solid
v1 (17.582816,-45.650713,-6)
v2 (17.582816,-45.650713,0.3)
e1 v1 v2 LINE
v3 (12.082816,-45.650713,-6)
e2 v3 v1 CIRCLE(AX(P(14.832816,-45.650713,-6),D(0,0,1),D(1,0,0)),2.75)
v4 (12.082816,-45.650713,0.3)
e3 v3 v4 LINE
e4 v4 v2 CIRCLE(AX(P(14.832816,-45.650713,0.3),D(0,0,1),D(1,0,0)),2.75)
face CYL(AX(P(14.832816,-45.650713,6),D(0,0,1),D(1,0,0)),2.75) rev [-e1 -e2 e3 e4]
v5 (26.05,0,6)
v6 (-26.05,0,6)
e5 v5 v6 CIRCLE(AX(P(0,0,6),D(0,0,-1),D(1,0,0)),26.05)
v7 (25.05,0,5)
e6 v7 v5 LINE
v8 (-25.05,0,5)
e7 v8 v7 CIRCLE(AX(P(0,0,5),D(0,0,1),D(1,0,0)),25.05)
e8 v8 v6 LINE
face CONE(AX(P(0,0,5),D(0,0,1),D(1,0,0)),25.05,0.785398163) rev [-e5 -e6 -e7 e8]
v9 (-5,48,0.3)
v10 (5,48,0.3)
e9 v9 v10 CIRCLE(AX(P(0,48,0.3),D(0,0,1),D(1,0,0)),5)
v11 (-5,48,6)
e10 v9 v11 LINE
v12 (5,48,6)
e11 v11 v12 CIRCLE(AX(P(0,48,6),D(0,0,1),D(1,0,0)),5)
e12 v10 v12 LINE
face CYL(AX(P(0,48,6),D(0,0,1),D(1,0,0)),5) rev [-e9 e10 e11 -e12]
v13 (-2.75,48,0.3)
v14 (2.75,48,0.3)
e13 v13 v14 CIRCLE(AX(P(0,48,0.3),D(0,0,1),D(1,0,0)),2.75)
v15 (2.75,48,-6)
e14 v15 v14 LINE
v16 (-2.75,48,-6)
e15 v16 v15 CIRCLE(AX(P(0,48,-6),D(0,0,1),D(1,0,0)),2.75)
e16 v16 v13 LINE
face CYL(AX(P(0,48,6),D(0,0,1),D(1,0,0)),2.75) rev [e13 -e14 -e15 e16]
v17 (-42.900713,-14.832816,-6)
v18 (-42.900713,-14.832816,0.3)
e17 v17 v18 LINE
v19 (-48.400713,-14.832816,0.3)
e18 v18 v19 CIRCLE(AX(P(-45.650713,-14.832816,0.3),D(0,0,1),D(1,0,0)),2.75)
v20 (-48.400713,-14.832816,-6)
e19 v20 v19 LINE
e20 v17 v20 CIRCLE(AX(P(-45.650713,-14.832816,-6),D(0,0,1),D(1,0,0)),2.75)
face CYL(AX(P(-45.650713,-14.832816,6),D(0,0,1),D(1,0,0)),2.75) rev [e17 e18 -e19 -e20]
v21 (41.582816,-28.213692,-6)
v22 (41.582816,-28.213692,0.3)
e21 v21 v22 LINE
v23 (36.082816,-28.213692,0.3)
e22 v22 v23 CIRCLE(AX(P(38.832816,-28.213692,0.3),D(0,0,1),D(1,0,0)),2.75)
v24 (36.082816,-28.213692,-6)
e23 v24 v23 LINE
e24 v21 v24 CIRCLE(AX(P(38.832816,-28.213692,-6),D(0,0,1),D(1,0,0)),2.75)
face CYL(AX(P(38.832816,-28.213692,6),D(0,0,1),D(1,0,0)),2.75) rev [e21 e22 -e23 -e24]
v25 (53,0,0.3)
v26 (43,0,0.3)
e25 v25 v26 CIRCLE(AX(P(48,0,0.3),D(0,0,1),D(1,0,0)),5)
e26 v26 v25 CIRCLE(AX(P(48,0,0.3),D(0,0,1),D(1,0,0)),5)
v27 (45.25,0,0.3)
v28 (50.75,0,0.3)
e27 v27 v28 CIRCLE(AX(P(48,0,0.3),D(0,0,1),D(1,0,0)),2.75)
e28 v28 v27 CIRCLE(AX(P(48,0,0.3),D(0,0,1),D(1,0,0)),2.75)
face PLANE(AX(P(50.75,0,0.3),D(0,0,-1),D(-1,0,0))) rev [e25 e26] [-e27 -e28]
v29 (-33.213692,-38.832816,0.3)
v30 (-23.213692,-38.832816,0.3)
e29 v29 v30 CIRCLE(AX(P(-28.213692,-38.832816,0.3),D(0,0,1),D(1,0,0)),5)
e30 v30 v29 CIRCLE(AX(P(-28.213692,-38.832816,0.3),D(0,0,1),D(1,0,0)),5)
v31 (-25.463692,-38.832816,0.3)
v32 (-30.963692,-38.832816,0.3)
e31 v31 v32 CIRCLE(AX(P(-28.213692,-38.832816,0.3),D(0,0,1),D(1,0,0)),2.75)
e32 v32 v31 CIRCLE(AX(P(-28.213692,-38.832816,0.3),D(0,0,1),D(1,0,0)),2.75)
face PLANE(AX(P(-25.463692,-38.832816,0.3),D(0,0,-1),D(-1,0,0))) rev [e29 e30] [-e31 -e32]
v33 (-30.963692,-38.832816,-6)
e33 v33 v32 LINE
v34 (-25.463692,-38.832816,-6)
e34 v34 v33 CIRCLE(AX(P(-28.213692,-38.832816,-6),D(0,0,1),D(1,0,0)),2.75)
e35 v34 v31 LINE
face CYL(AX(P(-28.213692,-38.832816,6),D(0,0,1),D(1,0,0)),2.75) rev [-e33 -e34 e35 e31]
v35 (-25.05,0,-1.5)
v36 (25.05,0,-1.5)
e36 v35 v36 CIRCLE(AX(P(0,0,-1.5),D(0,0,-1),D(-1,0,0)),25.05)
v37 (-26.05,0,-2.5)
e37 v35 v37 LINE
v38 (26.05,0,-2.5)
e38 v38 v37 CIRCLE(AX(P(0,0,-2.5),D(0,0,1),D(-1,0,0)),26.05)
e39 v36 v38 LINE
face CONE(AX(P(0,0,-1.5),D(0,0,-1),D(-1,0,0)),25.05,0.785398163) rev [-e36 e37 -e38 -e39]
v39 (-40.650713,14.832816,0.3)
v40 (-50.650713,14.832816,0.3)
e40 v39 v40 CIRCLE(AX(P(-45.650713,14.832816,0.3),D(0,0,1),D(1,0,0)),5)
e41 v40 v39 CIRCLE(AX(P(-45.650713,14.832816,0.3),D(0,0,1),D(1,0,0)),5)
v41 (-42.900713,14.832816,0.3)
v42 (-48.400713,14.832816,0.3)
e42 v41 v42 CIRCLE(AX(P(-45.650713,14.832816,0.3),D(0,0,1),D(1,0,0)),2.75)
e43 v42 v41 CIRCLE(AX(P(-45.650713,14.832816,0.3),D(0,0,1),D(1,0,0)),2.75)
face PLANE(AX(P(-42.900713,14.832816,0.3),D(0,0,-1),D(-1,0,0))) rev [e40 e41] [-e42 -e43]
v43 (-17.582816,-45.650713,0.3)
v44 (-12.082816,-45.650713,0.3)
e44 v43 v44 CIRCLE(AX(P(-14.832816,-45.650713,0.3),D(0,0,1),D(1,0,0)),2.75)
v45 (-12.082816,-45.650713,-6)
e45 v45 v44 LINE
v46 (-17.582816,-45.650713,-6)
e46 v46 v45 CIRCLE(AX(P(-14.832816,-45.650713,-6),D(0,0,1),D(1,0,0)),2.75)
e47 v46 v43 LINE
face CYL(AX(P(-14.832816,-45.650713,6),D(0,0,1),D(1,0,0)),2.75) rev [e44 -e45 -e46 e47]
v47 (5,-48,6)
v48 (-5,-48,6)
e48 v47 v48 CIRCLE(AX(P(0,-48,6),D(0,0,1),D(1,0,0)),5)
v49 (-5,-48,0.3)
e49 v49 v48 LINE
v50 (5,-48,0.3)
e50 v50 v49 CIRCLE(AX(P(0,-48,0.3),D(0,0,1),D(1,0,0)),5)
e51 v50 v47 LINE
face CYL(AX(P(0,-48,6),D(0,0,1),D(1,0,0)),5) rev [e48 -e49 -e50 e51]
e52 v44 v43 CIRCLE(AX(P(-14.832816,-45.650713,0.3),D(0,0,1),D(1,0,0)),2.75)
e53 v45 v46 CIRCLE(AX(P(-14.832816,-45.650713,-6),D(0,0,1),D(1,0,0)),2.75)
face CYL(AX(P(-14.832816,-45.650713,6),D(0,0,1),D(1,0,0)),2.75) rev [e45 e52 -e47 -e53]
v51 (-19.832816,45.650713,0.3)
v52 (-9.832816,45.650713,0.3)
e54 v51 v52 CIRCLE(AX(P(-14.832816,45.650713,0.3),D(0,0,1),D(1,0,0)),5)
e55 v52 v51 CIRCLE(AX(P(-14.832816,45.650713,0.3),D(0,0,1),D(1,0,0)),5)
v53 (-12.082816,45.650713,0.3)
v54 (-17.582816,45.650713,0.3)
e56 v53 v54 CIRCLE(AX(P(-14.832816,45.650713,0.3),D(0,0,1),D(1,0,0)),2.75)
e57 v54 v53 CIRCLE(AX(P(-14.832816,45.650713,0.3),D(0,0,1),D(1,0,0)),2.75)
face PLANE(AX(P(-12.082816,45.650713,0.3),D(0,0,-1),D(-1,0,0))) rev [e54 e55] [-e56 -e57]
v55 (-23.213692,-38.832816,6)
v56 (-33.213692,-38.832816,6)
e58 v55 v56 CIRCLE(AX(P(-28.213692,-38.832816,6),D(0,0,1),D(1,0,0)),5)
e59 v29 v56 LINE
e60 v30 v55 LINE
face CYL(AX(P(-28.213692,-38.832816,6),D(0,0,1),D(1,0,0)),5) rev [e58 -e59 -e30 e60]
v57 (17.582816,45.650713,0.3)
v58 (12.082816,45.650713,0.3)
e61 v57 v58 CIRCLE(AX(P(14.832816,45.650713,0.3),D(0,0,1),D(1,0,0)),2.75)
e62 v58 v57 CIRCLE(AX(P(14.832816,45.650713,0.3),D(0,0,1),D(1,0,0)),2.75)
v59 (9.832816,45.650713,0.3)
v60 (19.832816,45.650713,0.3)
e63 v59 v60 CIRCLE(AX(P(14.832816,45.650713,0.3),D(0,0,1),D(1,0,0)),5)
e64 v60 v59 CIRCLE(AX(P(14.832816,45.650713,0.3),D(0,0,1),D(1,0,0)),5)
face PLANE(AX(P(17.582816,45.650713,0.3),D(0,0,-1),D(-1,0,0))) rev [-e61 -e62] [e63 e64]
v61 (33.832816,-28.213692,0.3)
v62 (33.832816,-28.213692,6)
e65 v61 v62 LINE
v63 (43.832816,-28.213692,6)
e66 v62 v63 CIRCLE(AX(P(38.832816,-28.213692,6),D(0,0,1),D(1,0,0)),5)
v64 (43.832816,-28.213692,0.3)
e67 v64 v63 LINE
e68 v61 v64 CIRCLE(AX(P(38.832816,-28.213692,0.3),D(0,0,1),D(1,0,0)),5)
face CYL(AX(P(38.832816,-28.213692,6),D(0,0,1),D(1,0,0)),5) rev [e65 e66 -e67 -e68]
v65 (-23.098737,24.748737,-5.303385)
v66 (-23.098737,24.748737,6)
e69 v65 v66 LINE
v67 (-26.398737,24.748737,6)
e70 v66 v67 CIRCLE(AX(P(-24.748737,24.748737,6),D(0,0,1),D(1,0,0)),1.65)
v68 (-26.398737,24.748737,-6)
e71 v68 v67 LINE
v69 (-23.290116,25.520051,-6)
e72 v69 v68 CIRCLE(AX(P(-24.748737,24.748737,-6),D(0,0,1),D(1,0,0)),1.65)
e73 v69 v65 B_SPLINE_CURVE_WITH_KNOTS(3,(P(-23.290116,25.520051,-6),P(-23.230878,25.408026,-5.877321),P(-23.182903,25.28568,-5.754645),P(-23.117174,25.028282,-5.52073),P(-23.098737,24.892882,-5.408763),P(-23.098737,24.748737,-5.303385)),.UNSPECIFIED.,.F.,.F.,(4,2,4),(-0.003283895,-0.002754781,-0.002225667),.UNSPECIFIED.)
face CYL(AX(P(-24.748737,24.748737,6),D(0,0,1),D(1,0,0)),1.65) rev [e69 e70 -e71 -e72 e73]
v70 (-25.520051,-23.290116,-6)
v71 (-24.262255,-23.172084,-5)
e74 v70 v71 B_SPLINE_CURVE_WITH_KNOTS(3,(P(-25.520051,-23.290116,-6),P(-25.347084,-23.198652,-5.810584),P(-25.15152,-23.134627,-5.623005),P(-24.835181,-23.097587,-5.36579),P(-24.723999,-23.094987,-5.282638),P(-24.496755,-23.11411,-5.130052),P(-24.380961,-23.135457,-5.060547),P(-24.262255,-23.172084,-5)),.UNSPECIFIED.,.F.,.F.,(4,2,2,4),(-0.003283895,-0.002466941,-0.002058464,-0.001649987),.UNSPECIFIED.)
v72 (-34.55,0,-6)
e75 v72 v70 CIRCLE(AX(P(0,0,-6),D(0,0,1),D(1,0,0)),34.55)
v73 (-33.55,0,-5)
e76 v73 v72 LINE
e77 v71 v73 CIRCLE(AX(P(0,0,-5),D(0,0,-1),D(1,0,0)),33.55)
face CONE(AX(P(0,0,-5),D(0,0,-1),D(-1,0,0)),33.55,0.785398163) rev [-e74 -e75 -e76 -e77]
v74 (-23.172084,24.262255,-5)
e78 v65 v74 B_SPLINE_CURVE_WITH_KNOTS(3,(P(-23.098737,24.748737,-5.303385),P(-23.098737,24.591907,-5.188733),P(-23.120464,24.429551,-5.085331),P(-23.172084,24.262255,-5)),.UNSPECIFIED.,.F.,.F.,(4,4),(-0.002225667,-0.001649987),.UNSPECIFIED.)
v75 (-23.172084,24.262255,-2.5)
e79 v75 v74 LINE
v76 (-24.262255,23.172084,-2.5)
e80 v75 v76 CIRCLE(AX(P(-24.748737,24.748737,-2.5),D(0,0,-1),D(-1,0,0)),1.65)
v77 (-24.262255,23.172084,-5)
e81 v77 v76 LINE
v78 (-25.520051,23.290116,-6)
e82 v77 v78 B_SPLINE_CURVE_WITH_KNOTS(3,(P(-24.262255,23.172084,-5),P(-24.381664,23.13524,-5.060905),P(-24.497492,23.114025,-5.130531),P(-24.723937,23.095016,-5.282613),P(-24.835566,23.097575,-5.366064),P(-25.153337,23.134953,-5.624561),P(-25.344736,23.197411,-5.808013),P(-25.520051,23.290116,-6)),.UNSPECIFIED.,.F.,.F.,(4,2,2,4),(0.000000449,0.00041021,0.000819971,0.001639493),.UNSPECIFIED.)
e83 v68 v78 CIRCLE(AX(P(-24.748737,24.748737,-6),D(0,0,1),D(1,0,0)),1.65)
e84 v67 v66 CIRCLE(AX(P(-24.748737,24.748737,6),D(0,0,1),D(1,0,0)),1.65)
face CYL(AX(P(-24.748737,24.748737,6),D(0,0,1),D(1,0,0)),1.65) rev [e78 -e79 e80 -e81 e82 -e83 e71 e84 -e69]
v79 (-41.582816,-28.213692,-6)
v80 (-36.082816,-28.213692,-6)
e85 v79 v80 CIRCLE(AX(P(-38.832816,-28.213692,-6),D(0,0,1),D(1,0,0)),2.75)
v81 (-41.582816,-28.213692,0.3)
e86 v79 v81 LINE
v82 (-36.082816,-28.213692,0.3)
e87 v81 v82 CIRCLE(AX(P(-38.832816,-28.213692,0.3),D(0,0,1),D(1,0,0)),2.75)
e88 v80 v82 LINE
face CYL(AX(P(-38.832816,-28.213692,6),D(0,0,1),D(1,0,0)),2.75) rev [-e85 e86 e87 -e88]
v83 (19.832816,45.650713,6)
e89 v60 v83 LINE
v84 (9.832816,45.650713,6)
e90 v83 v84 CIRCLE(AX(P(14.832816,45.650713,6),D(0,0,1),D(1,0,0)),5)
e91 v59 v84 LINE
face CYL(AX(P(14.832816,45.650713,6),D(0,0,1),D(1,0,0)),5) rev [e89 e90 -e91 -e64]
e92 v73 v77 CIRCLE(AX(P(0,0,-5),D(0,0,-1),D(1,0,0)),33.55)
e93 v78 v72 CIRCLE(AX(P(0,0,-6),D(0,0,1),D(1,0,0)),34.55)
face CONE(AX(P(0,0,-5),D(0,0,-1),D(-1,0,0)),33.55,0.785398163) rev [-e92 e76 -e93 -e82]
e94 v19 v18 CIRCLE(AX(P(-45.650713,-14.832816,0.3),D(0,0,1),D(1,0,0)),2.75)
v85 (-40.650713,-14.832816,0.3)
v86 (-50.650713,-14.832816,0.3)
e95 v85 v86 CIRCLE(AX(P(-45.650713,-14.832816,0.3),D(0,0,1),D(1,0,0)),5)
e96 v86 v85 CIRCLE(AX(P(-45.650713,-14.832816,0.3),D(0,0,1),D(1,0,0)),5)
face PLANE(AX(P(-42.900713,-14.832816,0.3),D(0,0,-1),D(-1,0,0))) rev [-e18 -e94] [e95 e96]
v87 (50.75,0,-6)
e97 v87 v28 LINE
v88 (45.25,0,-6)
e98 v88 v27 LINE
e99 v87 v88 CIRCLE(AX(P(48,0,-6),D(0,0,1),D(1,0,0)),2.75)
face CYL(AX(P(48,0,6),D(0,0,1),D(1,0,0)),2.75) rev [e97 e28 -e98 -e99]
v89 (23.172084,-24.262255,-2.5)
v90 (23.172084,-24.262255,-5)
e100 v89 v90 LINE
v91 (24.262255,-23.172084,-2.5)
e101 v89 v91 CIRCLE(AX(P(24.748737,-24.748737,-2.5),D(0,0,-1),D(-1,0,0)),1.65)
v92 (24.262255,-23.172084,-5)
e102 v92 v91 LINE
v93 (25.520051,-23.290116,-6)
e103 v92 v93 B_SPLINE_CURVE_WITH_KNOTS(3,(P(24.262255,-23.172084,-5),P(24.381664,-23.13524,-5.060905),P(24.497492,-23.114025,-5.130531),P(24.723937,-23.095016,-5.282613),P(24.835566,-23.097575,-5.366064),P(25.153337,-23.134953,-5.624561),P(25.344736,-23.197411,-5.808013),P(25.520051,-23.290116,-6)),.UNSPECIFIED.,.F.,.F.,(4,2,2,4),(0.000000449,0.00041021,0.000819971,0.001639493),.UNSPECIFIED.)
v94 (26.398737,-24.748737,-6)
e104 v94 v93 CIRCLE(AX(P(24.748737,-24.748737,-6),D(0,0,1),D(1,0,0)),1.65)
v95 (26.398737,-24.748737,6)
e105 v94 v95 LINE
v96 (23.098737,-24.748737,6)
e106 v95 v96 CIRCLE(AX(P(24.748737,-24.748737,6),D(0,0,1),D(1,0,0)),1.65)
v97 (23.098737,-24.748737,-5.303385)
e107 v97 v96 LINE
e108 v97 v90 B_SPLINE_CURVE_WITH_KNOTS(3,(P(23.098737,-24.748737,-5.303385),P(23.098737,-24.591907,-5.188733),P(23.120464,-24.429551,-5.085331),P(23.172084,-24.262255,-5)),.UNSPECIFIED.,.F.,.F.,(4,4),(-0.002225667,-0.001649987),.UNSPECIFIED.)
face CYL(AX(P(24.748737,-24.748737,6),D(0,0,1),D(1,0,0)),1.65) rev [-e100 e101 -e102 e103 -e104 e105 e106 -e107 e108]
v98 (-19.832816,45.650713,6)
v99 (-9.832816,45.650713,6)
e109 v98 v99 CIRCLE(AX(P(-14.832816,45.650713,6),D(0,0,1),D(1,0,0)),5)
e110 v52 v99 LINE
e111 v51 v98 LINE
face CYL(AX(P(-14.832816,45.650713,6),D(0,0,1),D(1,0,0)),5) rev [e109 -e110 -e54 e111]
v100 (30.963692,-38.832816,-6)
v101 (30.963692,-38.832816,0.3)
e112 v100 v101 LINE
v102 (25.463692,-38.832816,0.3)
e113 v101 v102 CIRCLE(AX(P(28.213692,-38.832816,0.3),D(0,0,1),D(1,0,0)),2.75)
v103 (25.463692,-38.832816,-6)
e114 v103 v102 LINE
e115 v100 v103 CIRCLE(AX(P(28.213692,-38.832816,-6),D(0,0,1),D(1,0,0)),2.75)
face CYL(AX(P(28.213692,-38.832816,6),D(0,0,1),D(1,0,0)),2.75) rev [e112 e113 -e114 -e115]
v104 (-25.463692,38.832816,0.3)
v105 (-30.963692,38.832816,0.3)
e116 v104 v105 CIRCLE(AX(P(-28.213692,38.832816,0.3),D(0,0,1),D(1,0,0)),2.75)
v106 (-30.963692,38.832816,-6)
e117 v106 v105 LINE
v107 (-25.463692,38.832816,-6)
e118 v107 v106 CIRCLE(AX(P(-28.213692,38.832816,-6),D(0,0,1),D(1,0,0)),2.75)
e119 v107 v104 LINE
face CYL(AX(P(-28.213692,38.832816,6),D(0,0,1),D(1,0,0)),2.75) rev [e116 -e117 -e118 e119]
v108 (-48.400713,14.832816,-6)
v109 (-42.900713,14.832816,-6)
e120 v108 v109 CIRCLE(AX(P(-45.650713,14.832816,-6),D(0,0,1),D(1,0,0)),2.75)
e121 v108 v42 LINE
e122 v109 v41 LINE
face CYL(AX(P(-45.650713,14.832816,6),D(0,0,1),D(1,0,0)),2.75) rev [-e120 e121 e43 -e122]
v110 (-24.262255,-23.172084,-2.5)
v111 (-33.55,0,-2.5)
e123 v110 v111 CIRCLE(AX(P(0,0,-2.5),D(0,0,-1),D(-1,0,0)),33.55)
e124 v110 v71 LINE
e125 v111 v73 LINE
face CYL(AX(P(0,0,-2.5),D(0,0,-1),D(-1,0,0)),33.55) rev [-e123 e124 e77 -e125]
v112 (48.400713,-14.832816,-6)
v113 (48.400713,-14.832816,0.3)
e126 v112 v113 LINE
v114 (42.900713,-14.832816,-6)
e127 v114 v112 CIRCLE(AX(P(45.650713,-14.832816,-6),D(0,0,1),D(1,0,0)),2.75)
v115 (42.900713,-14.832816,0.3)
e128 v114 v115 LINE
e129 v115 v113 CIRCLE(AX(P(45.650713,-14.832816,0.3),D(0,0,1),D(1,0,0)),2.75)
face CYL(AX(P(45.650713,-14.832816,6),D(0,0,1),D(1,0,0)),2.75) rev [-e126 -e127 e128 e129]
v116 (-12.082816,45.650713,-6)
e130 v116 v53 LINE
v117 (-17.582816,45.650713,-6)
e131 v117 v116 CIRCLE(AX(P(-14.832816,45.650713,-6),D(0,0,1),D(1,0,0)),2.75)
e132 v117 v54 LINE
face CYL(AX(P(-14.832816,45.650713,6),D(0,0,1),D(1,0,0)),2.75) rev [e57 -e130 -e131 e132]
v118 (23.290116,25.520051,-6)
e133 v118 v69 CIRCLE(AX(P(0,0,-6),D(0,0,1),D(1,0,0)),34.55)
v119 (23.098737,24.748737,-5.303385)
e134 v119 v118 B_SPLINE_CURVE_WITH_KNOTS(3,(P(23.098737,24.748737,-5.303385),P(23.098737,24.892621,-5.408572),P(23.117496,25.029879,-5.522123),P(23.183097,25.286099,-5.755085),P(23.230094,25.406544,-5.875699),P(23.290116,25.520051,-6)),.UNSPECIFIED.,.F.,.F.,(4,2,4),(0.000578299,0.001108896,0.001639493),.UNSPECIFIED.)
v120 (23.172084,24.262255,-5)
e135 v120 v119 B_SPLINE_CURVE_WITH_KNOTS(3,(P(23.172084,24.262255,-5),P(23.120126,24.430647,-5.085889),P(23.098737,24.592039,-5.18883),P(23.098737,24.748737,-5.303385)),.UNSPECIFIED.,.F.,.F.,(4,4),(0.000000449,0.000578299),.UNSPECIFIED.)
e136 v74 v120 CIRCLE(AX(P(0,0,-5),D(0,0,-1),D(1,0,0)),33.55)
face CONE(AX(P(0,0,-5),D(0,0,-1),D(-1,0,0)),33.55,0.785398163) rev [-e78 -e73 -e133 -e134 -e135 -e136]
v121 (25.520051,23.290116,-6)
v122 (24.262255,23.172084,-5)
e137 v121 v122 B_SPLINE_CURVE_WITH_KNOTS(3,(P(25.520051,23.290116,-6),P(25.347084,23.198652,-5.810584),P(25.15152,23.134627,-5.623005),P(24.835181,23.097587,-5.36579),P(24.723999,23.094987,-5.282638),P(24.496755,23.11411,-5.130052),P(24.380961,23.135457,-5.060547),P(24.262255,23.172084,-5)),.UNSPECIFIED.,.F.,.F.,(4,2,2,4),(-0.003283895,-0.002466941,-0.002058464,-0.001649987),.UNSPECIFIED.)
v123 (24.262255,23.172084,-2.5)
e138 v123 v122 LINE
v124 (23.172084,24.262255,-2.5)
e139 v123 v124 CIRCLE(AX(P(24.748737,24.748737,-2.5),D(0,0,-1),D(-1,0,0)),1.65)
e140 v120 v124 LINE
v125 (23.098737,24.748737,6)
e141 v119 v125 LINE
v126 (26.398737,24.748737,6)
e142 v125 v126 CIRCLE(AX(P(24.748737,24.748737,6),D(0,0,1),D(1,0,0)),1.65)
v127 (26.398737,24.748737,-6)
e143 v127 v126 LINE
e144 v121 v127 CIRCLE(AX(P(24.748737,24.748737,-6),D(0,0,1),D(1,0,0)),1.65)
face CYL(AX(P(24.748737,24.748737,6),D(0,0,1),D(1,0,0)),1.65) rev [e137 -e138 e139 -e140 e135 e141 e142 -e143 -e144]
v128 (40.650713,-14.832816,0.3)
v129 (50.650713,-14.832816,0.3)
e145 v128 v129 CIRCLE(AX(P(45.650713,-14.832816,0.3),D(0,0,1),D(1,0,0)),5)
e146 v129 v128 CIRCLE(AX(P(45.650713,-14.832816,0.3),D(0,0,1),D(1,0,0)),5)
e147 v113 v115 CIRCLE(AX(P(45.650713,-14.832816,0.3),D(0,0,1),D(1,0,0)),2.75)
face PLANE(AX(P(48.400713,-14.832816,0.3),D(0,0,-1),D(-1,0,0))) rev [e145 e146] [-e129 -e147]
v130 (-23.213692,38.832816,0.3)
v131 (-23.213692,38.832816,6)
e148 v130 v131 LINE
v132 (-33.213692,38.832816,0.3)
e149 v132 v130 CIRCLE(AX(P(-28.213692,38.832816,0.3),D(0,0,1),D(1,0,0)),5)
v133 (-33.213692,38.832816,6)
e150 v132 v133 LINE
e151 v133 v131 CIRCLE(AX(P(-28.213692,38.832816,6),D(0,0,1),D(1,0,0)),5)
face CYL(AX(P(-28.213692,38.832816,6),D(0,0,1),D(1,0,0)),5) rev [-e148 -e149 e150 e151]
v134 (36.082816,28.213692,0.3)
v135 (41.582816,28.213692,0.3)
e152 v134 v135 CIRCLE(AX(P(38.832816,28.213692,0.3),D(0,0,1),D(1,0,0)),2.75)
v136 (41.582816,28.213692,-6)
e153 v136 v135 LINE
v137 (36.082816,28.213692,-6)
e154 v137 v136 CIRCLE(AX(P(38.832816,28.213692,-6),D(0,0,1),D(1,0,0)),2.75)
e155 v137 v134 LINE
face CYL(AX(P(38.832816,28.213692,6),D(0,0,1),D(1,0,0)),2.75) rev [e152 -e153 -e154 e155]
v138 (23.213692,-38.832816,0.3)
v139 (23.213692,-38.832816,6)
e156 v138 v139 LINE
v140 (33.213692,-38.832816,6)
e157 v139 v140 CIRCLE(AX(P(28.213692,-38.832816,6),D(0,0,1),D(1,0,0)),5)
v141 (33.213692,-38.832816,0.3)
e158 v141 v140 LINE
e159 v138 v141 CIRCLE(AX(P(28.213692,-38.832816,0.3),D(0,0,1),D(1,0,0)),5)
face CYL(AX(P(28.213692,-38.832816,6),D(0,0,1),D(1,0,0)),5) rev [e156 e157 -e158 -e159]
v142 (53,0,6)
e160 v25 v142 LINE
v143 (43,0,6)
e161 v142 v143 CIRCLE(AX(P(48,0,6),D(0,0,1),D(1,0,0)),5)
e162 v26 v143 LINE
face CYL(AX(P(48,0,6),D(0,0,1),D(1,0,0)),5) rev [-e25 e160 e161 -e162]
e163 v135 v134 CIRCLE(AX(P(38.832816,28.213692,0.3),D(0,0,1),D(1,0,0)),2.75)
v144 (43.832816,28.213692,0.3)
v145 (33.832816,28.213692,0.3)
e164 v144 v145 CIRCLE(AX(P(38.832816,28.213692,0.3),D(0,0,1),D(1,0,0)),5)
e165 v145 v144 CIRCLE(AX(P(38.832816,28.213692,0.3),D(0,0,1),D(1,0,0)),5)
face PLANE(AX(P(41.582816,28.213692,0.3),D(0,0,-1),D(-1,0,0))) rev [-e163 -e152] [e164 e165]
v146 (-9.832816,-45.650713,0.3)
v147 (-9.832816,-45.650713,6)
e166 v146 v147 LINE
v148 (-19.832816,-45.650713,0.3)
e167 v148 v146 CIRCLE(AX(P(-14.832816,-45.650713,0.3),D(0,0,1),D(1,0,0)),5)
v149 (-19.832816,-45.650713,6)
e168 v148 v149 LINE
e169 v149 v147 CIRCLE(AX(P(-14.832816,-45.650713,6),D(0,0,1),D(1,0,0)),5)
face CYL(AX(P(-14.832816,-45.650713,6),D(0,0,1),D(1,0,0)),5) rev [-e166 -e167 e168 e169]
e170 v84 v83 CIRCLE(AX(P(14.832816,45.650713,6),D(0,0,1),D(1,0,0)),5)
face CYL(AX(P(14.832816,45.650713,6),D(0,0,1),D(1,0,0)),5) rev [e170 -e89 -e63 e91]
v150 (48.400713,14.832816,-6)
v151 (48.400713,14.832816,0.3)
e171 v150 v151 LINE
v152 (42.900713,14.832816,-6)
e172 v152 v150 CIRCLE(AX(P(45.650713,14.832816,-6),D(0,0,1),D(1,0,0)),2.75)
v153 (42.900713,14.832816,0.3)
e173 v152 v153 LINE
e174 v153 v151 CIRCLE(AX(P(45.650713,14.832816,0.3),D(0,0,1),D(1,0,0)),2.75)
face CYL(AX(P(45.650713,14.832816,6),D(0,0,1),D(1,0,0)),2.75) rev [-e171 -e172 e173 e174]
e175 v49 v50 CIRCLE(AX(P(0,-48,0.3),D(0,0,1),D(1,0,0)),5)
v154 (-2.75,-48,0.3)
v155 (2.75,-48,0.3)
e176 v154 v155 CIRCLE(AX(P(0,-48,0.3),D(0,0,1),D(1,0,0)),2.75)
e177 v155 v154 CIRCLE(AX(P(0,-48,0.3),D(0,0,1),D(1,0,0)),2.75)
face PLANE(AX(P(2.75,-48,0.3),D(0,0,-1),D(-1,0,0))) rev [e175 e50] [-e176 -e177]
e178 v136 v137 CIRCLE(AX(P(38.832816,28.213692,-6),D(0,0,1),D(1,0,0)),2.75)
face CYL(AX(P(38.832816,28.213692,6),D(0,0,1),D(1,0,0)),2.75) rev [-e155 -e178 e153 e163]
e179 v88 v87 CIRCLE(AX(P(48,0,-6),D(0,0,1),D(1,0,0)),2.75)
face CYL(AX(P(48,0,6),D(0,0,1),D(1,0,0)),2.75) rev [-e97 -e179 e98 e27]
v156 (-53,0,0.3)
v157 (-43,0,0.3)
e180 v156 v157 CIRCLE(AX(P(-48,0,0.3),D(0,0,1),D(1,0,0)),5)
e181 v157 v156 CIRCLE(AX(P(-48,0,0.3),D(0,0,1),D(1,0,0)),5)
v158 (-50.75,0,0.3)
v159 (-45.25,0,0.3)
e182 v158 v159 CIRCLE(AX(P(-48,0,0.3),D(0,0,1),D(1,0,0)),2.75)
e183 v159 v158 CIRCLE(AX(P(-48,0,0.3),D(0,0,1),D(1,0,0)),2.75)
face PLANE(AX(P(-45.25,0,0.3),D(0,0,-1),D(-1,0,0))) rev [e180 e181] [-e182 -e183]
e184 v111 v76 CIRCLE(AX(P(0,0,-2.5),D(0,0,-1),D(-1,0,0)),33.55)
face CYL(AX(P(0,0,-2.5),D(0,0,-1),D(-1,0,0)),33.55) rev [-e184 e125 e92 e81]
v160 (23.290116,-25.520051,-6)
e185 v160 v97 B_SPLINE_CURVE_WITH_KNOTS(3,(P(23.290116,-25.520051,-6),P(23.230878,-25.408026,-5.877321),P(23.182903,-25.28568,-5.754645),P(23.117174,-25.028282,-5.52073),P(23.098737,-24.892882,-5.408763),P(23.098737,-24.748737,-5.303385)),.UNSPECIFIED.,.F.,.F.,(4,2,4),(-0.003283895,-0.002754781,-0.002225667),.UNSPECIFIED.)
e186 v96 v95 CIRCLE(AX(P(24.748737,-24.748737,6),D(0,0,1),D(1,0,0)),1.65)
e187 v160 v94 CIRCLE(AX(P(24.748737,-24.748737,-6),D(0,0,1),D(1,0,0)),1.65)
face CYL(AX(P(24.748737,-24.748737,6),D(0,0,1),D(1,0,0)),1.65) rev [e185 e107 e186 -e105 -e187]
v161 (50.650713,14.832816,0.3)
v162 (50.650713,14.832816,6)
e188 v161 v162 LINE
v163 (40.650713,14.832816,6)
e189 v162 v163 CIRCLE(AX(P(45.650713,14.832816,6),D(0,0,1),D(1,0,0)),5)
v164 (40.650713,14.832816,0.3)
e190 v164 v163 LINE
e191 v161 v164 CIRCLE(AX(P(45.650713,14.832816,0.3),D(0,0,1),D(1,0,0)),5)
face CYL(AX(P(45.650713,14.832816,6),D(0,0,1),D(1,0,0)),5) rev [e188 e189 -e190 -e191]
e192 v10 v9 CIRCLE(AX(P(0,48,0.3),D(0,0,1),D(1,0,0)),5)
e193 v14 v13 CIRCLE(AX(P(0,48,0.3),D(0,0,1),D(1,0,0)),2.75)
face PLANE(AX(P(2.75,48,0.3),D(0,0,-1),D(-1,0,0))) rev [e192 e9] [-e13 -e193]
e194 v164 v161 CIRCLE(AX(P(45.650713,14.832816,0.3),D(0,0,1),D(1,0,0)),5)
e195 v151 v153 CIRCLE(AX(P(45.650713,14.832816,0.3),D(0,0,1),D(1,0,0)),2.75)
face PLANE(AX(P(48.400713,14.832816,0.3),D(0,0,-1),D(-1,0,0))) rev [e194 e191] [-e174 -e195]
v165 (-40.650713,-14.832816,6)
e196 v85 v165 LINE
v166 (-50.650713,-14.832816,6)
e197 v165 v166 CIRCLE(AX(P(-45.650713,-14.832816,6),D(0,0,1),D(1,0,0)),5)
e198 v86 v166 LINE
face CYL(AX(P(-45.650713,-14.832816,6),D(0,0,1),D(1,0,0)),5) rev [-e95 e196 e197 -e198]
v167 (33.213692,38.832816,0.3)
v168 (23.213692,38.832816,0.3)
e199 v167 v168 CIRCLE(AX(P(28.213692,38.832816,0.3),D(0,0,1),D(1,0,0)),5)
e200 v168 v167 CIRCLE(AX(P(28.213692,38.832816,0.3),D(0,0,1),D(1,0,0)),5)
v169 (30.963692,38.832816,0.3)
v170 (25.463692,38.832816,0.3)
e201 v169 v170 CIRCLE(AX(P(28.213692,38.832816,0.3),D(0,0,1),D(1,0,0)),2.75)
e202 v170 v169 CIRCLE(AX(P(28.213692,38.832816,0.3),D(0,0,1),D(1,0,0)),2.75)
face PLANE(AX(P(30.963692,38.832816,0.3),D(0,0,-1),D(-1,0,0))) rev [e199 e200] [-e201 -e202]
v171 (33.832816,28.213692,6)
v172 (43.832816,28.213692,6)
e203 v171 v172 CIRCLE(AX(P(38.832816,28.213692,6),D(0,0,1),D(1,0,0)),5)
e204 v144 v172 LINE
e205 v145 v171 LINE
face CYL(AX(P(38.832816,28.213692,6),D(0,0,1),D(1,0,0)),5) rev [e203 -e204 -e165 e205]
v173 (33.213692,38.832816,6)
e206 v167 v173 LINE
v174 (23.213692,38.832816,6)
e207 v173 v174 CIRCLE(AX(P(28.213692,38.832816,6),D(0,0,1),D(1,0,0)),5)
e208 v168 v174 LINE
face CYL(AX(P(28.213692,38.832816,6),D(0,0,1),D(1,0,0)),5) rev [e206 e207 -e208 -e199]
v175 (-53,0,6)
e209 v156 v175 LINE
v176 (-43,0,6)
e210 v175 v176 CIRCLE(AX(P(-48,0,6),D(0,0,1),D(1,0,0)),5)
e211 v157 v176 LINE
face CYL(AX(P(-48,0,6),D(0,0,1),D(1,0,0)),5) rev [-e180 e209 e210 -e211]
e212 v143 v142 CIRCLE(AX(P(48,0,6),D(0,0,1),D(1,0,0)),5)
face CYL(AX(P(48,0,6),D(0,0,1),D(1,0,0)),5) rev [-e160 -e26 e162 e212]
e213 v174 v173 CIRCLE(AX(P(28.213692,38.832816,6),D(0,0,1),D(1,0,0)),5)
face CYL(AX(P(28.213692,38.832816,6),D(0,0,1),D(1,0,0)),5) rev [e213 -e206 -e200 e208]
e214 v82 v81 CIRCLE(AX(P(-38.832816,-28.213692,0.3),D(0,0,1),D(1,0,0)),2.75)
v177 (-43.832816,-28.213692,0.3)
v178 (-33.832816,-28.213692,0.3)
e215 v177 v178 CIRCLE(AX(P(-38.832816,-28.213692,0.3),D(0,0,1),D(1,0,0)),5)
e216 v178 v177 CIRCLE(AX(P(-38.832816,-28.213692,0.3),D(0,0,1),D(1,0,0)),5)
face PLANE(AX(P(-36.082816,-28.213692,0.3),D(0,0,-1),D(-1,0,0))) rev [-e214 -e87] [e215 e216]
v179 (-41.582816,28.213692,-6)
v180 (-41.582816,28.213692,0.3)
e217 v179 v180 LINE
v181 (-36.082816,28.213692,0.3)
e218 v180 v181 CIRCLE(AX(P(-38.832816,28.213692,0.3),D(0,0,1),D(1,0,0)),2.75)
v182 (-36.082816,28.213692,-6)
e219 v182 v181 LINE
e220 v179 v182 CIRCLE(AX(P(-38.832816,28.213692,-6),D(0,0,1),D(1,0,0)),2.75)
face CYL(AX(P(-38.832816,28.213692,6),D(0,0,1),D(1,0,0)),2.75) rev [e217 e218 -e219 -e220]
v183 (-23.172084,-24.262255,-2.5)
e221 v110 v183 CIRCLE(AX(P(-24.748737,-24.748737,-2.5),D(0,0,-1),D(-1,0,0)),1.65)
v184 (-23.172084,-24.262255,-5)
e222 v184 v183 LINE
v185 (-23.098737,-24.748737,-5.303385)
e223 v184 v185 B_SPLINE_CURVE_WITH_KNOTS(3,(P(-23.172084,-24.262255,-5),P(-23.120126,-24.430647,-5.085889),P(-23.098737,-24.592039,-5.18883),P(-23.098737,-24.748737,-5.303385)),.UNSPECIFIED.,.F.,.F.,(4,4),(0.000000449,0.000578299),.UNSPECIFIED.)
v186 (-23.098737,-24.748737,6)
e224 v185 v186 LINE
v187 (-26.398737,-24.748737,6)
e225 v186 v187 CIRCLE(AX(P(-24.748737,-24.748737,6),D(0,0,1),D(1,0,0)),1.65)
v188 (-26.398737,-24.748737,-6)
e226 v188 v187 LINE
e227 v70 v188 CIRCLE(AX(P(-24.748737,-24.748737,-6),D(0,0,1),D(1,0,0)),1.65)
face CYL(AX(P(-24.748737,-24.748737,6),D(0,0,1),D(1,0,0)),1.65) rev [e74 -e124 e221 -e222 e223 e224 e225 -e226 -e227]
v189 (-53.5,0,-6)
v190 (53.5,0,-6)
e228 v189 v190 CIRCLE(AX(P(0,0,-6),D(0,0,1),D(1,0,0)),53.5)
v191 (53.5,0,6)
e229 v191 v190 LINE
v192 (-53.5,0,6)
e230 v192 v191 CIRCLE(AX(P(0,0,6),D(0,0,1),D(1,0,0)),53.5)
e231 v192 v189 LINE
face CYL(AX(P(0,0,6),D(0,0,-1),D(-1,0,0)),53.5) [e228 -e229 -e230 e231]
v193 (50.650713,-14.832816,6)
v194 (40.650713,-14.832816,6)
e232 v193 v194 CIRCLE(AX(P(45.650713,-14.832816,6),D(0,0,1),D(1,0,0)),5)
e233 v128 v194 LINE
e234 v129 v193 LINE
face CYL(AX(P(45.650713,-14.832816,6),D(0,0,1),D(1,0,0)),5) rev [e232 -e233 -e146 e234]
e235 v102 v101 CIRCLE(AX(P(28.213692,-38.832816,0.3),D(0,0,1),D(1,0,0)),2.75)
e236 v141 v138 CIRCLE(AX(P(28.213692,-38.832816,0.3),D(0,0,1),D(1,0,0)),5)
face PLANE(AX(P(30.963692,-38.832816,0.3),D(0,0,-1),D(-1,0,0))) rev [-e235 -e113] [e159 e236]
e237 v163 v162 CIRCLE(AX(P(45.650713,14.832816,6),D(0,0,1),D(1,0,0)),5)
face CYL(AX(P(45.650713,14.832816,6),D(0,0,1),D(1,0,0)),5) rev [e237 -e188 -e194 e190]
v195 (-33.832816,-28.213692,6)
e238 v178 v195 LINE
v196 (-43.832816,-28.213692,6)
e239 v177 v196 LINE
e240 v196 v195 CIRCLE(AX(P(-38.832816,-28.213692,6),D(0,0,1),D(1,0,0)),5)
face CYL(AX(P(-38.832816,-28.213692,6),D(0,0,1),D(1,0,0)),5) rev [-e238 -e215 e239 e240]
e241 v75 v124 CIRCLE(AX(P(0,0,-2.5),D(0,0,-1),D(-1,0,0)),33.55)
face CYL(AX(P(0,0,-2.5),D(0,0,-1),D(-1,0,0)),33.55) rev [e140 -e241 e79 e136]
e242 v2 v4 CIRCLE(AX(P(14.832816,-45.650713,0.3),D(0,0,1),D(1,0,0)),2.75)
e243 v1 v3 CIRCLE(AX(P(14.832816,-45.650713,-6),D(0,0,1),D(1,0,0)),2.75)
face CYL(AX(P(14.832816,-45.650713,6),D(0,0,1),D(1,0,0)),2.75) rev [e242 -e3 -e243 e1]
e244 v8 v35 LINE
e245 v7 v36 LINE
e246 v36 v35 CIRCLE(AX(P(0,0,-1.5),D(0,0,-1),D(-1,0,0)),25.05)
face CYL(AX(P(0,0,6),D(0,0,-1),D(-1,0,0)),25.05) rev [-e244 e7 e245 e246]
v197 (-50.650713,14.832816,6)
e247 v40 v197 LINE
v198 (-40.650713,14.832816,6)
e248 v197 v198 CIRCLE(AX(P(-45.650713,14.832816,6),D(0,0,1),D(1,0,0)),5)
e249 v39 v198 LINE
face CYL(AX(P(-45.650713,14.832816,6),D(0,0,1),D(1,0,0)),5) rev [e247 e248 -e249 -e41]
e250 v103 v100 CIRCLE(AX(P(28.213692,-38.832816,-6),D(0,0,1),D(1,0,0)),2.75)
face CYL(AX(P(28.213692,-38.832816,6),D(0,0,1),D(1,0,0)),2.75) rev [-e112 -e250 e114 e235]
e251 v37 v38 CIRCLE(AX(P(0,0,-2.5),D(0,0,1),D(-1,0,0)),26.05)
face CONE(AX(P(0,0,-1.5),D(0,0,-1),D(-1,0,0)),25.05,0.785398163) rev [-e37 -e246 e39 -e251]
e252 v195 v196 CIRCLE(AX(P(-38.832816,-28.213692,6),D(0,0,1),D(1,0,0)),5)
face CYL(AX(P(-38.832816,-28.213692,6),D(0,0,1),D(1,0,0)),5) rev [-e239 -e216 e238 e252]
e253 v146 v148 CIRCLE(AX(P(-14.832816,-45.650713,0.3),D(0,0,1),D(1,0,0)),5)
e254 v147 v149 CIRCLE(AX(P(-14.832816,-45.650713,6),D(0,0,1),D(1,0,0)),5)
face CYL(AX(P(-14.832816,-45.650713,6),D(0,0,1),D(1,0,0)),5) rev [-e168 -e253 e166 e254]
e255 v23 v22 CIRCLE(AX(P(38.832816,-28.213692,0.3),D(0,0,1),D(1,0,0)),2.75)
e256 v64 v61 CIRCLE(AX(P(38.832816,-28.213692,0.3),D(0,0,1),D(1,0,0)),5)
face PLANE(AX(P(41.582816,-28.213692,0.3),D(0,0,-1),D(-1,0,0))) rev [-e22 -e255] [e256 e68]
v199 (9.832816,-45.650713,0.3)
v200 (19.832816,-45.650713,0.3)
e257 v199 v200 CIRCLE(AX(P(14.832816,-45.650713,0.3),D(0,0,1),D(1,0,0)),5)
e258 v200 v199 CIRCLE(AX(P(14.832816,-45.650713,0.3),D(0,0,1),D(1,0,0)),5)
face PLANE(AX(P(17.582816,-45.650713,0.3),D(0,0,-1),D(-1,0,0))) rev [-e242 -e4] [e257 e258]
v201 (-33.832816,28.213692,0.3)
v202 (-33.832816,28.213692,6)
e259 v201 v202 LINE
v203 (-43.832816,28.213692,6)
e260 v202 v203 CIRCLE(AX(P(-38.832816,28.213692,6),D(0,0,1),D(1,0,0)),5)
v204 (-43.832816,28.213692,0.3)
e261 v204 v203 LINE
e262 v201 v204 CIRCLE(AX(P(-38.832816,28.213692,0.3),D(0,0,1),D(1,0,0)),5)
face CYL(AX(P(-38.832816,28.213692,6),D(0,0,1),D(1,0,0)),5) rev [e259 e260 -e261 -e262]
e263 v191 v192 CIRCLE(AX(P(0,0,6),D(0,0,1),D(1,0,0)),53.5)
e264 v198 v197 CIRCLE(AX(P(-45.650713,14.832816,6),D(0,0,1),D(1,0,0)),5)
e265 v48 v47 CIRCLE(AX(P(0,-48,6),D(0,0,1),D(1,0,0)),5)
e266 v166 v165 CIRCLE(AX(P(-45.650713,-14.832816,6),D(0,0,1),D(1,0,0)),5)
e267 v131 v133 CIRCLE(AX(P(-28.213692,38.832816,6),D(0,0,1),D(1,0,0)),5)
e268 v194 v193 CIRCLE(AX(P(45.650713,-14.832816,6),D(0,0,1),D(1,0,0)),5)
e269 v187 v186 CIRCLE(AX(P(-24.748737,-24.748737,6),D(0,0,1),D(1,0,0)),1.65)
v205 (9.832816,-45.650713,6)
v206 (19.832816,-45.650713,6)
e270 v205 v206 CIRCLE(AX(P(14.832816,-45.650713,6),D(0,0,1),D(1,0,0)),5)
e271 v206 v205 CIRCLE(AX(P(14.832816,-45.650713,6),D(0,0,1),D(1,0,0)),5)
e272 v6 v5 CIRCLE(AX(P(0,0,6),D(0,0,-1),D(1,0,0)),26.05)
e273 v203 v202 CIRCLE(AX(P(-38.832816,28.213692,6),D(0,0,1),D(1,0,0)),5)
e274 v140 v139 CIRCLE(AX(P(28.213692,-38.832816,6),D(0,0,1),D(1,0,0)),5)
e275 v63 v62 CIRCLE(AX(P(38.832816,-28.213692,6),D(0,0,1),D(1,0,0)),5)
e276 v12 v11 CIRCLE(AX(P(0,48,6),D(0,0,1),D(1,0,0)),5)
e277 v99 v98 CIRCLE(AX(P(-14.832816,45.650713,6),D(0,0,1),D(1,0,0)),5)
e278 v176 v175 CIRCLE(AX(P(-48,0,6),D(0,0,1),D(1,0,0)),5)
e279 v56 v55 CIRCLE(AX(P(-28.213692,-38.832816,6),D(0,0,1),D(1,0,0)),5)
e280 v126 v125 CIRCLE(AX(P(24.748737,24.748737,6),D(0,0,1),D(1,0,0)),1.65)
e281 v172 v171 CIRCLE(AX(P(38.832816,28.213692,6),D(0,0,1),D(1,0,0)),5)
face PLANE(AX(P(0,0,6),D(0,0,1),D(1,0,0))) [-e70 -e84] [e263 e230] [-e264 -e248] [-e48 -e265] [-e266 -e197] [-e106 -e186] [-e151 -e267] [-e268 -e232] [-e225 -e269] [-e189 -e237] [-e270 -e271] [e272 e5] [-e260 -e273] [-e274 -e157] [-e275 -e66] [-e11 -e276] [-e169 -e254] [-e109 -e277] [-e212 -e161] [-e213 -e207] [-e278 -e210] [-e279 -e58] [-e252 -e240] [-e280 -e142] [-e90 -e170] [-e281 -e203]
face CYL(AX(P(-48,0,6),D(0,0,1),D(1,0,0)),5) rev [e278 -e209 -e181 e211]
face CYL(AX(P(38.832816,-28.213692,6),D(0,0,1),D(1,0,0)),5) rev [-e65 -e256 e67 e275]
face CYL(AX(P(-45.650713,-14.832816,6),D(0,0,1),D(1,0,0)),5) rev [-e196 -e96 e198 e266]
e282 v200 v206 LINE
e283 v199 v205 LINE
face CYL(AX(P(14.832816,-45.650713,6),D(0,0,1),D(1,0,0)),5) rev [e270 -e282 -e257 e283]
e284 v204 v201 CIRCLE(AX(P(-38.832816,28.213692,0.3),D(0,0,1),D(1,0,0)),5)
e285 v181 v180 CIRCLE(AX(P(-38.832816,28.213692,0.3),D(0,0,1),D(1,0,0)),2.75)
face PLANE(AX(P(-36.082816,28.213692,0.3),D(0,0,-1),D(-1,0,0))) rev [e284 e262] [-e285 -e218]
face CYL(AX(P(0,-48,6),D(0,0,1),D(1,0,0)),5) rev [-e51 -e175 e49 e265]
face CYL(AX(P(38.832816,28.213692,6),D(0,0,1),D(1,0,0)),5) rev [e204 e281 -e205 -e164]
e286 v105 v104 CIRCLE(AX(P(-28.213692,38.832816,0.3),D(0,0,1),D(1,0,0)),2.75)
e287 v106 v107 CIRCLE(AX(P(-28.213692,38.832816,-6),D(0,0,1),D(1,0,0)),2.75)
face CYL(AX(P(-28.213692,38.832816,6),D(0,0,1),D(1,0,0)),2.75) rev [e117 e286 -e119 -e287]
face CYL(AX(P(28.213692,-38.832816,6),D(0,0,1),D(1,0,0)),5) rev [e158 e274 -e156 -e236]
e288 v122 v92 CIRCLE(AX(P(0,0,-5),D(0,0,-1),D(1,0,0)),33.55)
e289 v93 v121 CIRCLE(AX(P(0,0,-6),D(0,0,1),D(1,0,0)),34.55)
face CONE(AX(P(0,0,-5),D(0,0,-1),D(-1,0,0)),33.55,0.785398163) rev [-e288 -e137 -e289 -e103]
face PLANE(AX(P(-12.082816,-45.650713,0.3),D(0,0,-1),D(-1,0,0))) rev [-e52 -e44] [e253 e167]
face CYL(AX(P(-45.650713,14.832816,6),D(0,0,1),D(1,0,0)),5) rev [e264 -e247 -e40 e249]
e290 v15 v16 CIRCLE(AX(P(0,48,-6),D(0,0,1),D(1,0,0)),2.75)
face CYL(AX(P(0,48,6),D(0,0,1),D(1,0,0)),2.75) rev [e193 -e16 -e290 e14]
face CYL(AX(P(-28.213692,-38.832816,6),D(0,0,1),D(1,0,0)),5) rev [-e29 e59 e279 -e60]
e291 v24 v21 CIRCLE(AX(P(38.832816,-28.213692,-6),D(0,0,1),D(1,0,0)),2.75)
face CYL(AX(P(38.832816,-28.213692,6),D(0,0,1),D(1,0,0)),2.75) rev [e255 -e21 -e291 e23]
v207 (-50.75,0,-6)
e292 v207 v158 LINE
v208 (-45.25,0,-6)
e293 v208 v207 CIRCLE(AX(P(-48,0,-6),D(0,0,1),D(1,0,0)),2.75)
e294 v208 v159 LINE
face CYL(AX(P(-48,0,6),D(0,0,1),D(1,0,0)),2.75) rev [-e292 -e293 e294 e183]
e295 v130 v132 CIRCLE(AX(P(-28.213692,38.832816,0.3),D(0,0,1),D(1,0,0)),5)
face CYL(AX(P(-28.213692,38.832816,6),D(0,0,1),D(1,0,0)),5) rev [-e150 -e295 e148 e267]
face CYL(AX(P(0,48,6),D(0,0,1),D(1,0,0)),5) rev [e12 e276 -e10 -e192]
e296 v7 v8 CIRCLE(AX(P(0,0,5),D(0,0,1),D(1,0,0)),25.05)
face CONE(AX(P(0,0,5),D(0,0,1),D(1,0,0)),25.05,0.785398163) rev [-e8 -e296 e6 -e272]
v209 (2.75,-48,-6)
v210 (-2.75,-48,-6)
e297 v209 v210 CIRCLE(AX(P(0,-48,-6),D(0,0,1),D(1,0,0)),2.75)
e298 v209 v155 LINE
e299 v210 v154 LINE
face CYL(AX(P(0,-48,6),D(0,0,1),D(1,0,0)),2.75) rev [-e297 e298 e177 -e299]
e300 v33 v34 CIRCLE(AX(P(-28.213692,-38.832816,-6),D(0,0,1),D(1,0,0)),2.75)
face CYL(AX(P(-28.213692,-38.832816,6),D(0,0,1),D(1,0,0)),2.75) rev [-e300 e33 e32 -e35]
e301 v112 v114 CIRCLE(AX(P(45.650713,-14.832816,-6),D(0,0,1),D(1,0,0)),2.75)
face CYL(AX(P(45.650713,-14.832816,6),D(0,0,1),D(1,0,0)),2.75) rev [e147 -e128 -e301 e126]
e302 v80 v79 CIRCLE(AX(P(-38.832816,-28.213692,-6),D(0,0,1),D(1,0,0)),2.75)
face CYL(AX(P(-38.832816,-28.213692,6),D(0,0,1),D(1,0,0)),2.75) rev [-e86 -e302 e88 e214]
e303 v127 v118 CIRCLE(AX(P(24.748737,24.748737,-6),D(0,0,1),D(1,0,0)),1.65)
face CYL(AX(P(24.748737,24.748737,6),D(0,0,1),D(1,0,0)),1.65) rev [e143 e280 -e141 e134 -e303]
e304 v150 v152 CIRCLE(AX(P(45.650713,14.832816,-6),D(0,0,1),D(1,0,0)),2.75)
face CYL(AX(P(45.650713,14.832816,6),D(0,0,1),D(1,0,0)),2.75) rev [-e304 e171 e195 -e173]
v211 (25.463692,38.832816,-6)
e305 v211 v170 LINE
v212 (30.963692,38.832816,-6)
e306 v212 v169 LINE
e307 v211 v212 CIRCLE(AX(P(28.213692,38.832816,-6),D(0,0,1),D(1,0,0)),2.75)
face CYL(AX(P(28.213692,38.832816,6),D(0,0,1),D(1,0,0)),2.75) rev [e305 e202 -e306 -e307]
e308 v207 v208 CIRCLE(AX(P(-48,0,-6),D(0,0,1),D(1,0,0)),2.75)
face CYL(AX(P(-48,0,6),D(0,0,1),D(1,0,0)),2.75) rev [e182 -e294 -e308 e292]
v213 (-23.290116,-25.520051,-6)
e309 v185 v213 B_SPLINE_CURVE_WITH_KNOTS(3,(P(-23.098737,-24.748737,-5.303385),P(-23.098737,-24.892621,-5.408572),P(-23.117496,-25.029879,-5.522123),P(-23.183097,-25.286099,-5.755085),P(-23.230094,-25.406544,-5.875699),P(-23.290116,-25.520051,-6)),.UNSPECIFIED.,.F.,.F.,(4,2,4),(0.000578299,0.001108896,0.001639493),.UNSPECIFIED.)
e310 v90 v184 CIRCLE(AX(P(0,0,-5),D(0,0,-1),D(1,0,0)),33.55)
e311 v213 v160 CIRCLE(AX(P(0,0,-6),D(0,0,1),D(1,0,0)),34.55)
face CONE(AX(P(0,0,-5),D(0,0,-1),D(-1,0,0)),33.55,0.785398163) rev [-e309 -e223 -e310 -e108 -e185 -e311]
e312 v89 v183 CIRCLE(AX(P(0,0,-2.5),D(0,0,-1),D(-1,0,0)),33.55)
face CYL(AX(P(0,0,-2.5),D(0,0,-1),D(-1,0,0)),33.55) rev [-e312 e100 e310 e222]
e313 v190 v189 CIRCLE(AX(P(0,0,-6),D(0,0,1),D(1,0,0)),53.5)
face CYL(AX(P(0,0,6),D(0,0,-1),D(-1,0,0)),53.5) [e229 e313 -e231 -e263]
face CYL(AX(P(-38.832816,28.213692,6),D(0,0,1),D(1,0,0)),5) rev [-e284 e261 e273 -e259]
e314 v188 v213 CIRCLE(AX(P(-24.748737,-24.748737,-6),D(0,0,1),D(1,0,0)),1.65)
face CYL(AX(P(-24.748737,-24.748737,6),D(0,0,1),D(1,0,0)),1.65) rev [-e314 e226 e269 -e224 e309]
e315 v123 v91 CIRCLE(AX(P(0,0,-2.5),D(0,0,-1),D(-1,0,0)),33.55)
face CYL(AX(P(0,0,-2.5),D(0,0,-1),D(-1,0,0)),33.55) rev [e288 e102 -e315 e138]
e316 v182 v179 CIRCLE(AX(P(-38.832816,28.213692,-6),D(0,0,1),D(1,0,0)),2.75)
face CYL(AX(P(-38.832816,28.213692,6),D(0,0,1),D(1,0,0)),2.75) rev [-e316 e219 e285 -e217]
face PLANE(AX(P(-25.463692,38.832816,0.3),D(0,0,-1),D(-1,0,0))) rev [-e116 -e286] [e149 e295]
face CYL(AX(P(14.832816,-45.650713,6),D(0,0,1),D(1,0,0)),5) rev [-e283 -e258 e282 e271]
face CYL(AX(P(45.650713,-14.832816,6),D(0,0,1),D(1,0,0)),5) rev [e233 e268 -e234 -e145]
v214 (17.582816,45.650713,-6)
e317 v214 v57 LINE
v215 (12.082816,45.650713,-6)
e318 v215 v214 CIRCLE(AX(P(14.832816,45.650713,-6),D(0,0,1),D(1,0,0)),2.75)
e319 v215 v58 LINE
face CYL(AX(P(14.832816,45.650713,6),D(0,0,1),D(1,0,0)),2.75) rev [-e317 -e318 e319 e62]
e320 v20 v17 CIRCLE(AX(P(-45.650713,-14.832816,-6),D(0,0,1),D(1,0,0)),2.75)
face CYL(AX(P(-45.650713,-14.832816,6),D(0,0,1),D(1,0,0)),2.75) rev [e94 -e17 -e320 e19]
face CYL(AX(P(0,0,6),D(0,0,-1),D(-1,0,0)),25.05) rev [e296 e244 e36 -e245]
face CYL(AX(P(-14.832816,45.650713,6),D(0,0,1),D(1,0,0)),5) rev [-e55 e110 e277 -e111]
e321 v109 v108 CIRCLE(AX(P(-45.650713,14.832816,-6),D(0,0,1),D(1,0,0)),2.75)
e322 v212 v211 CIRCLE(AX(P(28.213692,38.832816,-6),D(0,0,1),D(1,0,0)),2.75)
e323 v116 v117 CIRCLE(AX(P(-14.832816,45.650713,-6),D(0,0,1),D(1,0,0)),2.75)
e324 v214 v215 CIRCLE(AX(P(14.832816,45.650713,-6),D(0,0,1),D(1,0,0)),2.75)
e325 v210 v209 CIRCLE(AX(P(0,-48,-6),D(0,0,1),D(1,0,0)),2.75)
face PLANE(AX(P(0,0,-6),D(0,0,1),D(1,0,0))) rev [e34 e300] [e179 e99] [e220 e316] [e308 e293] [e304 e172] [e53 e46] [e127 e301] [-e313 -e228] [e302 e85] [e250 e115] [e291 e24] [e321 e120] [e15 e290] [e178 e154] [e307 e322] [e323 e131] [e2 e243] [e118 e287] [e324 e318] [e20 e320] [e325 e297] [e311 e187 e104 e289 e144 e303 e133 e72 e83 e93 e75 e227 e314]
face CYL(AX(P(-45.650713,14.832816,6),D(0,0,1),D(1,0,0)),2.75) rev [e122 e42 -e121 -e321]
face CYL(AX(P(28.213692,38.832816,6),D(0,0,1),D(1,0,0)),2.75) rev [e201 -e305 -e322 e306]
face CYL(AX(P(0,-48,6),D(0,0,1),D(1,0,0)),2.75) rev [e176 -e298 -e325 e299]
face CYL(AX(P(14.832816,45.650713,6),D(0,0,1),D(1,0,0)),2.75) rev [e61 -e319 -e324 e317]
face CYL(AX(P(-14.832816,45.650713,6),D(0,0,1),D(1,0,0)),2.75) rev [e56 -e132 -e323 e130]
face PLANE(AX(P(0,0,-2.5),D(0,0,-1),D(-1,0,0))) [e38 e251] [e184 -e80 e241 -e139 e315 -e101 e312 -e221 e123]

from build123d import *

# Parameters (mm, degrees)
SKETCH_1_R                = 53.5
SKETCH_1_R_2              = 25.05
EXTRUDE_1_DEPTH           = 6
HOLE_WIZARD_1_D           = 5.5
HOLE_WIZARD_1_CBORE_D     = 10
HOLE_WIZARD_1_CBORE_DEPTH = 5.7
SKETCH_6_R                = 33.55
CUT_EXTRUDE_1_DEPTH       = 3.5
CHAMFER_1_SIZE            = 1
HOLE_WIZARD_M4_1_D        = 3.3
PATTERN_CIRCULAR_1_COUNT  = 20
PATTERN_CIRCULAR_2_COUNT  = 4


with BuildPart() as part:
    # 草图1 → 凸台-拉伸1 (new, symmetric)
    with BuildSketch(Plane.XY):
        Circle(SKETCH_1_R)
        Circle(SKETCH_1_R_2, mode=Mode.SUBTRACT)
    extrude(amount=EXTRUDE_1_DEPTH, both=True)

    # 打孔尺寸(%根据)内六角圆柱头螺钉的类型1 (through all)
    with Locations(Plane.XY.offset(6)):
        with Locations((0, 48)):
            hole_wizard_1 = CounterBoreHole(HOLE_WIZARD_1_D / 2, HOLE_WIZARD_1_CBORE_D / 2, HOLE_WIZARD_1_CBORE_DEPTH)

    # 草图6 → 切除-拉伸1 (cut)
    with BuildSketch(Plane(origin=(0, 0, -6), x_dir=(-1, 0, 0), z_dir=(0, 0, -1))):
        Circle(SKETCH_6_R)
    extrude(amount=-CUT_EXTRUDE_1_DEPTH, mode=Mode.SUBTRACT)

    # 倒角1
    chamfer_1_edges = [part.edges().sort_by_distance(p)[0] for p in [
        (-25.05, 0, -2.5),
        (33.55, 0, -6),
        (-25.05, 0, 6),
    ]]
    chamfer(chamfer_1_edges, length=CHAMFER_1_SIZE)

    # M4 螺纹孔1 (through all)
    with Locations(Plane.XY.offset(6)):
        with Locations((24.748737342, 24.748737342)):
            hole_wizard_m4_1 = Hole(HOLE_WIZARD_M4_1_D / 2)

    # 阵列(圆周)1: 打孔尺寸(%根据)内六角圆柱头螺钉的类型1 ×20 about axis
    pattern_circular_1_axis = Axis((0, 0, 0), (0, 0, 1))
    for i in range(1, PATTERN_CIRCULAR_1_COUNT):
        add(hole_wizard_1.rotate(pattern_circular_1_axis, i * 360 / PATTERN_CIRCULAR_1_COUNT), mode=Mode.SUBTRACT)

    # 阵列(圆周)2: M4 螺纹孔1 ×4 about axis
    pattern_circular_2_axis = Axis((0, 0, 0), (0, 0, 1))
    for i in range(1, PATTERN_CIRCULAR_2_COUNT):
        add(hole_wizard_m4_1.rotate(pattern_circular_2_axis, i * 360 / PATTERN_CIRCULAR_2_COUNT), mode=Mode.SUBTRACT)


solid = part.part
